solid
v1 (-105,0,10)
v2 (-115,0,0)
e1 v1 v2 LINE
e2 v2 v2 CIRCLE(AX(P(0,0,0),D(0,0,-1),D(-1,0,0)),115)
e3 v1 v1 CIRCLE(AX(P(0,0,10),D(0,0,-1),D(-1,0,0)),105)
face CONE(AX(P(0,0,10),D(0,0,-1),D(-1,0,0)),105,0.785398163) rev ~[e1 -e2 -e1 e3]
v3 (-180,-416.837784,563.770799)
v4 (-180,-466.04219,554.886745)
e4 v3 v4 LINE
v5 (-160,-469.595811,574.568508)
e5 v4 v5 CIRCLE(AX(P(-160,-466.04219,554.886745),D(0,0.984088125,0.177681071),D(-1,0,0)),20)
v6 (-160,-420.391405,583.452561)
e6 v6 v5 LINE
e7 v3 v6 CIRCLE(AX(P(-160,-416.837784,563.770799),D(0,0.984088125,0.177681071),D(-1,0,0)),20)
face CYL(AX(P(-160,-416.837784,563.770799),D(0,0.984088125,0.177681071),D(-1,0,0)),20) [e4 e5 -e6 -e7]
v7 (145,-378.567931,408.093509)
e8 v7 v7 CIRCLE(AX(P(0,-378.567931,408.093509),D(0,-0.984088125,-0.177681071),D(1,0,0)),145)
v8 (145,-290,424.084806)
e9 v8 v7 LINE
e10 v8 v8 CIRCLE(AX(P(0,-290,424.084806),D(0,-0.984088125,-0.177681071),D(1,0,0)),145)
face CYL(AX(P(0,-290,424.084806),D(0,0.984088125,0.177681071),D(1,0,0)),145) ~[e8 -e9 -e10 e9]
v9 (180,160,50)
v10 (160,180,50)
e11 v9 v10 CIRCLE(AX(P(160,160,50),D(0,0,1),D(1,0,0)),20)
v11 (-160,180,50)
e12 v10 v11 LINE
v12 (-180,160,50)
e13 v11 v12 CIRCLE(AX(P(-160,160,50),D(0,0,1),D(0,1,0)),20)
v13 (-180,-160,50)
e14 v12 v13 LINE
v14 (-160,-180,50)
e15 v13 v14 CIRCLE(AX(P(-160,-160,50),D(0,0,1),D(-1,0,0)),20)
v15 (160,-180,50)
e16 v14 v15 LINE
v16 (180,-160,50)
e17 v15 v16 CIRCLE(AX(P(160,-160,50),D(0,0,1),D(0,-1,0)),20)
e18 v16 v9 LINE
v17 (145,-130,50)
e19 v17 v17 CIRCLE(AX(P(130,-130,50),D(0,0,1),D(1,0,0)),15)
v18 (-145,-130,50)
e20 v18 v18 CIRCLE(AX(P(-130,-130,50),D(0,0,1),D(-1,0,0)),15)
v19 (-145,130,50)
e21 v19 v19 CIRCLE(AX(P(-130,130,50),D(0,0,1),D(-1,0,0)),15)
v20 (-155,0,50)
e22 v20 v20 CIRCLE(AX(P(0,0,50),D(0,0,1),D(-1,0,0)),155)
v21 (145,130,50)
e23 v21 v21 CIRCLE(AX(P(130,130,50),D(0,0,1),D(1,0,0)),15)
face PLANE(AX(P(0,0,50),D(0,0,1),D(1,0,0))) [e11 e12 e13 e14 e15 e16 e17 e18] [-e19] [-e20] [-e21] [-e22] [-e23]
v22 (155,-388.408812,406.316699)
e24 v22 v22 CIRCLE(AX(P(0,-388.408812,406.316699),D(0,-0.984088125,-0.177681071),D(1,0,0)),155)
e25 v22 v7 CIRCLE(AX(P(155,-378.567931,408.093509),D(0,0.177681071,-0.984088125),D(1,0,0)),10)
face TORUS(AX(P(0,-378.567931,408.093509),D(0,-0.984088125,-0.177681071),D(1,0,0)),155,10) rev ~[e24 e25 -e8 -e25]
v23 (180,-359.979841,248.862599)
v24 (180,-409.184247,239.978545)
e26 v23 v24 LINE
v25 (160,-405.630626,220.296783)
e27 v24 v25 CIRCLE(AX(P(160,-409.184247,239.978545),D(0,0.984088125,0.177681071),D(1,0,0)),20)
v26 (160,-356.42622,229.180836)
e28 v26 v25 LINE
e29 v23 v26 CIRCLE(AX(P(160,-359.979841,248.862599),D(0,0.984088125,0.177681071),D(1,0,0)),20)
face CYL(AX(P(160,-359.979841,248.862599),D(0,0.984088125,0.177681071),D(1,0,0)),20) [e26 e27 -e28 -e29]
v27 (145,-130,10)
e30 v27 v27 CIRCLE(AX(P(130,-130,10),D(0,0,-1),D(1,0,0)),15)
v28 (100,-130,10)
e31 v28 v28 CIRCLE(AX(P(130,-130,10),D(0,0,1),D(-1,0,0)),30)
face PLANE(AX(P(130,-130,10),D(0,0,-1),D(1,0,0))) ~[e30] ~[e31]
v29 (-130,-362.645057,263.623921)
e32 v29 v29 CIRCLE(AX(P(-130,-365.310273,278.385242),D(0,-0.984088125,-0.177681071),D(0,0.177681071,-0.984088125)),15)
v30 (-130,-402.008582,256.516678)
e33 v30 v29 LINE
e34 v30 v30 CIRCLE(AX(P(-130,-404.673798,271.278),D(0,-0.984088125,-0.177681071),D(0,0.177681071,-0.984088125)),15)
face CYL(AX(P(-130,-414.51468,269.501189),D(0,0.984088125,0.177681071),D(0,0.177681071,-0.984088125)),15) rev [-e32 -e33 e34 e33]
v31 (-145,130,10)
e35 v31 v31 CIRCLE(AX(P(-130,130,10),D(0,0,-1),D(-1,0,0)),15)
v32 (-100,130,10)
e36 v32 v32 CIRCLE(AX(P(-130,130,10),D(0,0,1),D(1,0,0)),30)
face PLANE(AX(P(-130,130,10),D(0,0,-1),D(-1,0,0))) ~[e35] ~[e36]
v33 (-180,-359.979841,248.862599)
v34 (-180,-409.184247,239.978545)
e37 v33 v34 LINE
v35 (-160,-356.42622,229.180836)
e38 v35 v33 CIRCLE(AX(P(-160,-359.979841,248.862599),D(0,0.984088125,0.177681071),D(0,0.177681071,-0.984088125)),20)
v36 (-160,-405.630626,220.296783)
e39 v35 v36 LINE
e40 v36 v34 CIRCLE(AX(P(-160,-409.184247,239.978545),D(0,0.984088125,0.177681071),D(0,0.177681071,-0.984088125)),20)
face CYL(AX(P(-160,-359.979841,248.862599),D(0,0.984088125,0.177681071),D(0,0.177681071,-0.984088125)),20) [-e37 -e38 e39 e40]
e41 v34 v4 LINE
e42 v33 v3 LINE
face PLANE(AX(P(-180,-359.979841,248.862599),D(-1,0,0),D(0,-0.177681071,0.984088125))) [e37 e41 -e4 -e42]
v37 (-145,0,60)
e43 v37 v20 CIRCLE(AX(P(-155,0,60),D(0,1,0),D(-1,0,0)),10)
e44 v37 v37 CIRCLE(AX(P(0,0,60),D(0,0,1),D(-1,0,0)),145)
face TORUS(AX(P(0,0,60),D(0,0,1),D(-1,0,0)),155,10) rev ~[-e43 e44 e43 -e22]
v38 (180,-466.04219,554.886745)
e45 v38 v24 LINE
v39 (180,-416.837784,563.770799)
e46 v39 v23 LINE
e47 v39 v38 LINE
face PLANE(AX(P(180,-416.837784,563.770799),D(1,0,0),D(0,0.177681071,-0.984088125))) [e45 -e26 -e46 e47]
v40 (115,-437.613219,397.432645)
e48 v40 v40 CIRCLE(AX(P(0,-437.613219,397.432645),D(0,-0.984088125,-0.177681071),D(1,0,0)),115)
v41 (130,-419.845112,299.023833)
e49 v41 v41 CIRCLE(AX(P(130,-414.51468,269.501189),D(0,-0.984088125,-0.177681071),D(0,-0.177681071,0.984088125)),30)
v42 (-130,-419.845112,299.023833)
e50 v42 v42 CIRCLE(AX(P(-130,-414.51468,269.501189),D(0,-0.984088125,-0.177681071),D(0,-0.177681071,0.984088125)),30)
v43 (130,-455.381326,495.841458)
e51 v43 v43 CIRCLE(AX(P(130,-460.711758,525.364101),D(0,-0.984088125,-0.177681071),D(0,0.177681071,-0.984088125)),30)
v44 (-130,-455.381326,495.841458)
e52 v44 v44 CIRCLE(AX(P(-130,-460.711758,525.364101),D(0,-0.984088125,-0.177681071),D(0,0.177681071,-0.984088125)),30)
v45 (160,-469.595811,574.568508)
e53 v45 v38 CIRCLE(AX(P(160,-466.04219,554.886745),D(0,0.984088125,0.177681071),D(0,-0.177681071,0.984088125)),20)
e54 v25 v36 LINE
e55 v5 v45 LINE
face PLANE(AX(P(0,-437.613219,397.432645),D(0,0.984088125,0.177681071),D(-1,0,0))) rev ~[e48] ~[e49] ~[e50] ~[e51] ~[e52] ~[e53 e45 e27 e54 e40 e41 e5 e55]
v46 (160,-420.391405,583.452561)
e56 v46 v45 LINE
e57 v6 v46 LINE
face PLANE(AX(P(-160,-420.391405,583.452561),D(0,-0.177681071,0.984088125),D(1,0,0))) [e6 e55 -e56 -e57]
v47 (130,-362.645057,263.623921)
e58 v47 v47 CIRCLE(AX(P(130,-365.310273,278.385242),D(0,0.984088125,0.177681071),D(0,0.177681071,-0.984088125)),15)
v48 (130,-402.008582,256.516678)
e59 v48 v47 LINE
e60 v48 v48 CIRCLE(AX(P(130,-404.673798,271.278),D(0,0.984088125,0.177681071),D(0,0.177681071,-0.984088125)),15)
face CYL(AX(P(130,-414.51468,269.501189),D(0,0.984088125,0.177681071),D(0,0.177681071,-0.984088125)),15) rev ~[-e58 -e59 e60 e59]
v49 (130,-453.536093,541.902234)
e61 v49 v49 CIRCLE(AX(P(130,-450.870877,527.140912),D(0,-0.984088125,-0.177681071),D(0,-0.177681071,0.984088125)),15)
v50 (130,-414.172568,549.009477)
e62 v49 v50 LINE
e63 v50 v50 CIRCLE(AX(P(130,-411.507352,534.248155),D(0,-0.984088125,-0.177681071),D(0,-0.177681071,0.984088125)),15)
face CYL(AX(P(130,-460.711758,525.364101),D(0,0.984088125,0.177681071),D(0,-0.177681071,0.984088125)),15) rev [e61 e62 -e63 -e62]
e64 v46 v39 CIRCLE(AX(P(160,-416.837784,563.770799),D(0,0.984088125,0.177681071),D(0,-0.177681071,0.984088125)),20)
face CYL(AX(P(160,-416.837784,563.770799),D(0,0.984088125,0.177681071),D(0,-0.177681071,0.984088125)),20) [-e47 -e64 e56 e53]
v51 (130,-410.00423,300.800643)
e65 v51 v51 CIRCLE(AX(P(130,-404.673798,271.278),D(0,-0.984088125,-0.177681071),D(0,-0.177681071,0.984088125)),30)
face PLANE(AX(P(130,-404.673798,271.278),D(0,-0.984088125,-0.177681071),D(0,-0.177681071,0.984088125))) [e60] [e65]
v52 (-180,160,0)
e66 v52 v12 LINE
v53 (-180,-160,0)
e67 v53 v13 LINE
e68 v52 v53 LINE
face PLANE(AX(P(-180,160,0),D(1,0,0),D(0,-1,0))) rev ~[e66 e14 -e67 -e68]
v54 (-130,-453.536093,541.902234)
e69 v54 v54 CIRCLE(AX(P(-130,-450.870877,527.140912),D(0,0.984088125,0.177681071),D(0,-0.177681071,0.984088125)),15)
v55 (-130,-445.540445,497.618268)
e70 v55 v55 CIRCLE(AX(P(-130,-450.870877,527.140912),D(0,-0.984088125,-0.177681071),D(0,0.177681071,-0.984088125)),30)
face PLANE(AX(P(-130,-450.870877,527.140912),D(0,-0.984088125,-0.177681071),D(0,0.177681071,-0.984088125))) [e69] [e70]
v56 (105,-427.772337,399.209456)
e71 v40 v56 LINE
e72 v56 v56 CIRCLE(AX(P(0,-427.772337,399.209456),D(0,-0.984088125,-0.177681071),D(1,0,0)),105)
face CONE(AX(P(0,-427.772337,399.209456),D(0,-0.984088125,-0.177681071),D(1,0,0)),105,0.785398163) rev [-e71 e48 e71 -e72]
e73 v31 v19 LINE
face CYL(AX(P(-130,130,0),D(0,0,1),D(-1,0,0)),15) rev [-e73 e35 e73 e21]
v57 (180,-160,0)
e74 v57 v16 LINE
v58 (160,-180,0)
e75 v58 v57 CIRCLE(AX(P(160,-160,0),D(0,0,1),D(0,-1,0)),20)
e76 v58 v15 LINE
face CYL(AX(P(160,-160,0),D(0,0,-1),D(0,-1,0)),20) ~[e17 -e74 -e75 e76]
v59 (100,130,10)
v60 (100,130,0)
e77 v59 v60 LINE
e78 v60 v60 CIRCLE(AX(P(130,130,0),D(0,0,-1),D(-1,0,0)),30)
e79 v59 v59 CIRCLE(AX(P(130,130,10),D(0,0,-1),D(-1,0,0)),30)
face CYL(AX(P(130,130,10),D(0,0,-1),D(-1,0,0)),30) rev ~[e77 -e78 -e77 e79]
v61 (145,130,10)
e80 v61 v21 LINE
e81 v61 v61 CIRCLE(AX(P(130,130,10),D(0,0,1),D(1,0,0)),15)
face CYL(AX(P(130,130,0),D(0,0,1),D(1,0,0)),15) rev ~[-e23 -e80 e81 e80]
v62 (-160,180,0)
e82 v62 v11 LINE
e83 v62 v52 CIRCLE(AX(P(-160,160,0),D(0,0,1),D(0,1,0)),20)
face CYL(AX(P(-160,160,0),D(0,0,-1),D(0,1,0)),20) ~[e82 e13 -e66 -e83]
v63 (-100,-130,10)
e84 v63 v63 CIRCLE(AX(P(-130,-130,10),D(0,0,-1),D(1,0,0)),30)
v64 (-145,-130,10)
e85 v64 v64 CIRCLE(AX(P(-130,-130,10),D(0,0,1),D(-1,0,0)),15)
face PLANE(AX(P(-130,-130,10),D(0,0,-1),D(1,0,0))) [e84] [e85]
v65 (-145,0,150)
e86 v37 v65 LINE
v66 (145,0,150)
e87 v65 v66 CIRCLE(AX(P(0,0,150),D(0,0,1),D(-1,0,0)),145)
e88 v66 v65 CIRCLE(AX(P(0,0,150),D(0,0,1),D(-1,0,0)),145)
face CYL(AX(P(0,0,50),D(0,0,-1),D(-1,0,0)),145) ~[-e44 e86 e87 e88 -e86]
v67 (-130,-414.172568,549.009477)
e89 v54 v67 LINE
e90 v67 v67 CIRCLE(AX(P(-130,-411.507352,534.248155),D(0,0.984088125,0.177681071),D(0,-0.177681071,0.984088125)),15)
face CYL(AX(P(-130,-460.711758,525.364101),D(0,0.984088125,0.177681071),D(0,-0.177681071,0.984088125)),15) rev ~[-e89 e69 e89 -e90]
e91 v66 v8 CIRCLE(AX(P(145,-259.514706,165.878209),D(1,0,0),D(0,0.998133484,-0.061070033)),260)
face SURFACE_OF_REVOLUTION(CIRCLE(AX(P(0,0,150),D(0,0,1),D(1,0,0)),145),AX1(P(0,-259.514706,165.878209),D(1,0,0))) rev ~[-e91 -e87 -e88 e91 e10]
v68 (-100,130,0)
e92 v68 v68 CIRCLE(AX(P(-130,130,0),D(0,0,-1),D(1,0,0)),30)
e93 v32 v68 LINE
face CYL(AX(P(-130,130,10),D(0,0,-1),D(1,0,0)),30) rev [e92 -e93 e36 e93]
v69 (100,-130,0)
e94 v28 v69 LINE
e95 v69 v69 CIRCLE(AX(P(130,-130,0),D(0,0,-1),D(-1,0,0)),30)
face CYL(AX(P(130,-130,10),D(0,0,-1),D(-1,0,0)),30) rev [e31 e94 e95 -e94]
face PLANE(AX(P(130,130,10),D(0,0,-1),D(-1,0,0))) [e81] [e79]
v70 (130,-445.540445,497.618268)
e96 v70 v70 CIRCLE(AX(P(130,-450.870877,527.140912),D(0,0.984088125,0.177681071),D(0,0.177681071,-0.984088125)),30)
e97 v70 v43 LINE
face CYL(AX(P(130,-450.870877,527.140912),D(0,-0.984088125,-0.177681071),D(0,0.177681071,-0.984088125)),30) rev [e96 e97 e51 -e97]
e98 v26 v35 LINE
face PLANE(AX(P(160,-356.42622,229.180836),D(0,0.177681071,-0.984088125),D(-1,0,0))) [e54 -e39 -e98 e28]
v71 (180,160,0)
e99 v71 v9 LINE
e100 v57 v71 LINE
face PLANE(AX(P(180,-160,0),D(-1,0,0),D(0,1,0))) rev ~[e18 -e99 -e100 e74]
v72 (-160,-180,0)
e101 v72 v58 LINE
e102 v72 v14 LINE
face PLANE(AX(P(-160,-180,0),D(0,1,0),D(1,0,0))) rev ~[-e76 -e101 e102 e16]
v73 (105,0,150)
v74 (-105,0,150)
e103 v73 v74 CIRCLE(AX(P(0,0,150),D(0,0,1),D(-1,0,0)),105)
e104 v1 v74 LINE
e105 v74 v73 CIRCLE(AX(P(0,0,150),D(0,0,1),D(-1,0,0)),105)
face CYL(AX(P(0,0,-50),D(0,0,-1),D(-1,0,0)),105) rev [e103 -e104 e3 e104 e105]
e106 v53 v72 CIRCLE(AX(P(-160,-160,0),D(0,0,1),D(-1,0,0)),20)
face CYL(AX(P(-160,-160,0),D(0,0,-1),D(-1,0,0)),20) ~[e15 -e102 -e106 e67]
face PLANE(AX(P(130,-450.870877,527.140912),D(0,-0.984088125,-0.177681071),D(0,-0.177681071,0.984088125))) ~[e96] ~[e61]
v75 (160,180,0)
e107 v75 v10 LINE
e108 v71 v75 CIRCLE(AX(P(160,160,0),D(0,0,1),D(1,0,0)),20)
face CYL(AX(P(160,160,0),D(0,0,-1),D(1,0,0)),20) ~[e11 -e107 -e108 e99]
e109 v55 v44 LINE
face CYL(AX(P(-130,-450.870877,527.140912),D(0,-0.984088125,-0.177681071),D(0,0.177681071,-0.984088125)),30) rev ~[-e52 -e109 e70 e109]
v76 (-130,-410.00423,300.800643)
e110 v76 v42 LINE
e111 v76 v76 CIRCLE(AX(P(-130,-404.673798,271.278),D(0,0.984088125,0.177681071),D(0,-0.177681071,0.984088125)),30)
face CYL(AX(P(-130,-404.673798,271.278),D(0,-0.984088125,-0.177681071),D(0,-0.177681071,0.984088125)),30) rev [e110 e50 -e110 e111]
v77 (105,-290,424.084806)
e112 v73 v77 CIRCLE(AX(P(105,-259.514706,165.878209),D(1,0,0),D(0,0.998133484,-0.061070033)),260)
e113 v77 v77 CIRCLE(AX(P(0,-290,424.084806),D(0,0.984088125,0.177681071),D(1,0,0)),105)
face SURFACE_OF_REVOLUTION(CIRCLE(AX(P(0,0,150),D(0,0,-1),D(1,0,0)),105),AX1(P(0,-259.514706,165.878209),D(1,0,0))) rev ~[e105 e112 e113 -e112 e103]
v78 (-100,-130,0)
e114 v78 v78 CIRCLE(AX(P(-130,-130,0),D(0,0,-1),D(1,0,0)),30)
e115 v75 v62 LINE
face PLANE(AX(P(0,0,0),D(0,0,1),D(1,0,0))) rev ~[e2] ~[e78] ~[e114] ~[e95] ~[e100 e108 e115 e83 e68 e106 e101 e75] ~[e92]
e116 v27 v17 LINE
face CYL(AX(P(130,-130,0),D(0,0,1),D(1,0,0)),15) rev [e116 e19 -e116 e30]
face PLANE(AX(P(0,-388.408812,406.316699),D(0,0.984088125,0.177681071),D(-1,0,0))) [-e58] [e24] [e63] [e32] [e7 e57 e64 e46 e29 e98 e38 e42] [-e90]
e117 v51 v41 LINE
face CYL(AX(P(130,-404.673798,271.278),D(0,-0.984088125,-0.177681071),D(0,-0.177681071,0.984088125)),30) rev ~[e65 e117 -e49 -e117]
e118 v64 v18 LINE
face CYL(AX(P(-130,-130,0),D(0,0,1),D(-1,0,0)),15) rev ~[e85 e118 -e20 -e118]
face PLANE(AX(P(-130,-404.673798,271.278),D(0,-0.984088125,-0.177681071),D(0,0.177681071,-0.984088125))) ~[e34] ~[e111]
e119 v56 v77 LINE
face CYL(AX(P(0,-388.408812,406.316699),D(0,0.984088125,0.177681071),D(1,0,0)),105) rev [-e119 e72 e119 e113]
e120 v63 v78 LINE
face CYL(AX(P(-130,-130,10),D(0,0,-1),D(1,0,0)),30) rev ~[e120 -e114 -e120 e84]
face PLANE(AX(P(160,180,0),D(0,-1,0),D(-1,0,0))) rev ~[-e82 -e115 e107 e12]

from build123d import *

# Parameters (mm, degrees)
INLET_FLANGE_360X360X50_DEPTH                    = 50
INLET_HUB_SKETCH_R                               = 145
INLET_HUB_SKETCH_R_2                             = 105
INLET_HUB_290_DEPTH                              = 100
INLET_START                                      = -100
INLET_BORE_SKETCH_R                              = 105
INLET_BORE_CUT_DEPTH                             = 100
INLET_FLANGE_CHAMFER_10_SIZE                     = 10
INLET_FLANGE_C_BORE_HOLE_30_D                    = 30
INLET_FLANGE_C_BORE_HOLE_30_CBORE_D              = 60
INLET_FLANGE_C_BORE_HOLE_30_CBORE_DEPTH          = 10
INLET_HOLES_MIRROR_RIGHT_COPY_1_D                = 30
INLET_HOLES_MIRROR_RIGHT_COPY_1_CBORE_D          = 60
INLET_HOLES_MIRROR_RIGHT_COPY_1_CBORE_DEPTH      = 10
BEND_PROFILE_SKETCH_R                            = 145
BEND_PROFILE_SKETCH_R_2                          = 105
OUTLET_HUB_SKETCH_R                              = 145
OUTLET_HUB_SKETCH_R_2                            = 105
OUTLET_HUB_290_DEPTH                             = 100
OUTLET_FLANGE_SKETCH_R                           = 105
OUTLET_FLANGE_360X360X50_DEPTH                   = 50
OUTLET_FLANGE_C_BORE_HOLE_30_D                   = 30
OUTLET_FLANGE_C_BORE_HOLE_30_DEPTH               = 50
OUTLET_FLANGE_C_BORE_HOLE_30_CBORE_D             = 60
OUTLET_FLANGE_C_BORE_HOLE_30_CBORE_DEPTH         = 10
OUTLET_HOLES_MIRROR_MID_PLANE_COPY_1_D           = 30
OUTLET_HOLES_MIRROR_MID_PLANE_COPY_1_DEPTH       = 50
OUTLET_HOLES_MIRROR_MID_PLANE_COPY_1_CBORE_D     = 60
OUTLET_HOLES_MIRROR_MID_PLANE_COPY_1_CBORE_DEPTH = 10
HUB_FILLETS_R10_R                                = 10
OUTLET_FLANGE_CHAMFER_10_SIZE                    = 10


with BuildPart() as part:
    # Inlet Flange Sketch → Inlet Flange 360x360x50 (new body)
    with BuildSketch(Plane.XY):
        with BuildLine():
            Line((-160, -180), (160, -180))
            ThreePointArc((160, -180), (174.142135624, -174.142135624), (180, -160))
            Line((180, -160), (180, 160))
            ThreePointArc((180, 160), (174.142135624, 174.142135624), (160, 180))
            Line((160, 180), (-160, 180))
            ThreePointArc((-160, 180), (-174.142135624, 174.142135624), (-180, 160))
            Line((-180, 160), (-180, -160))
            ThreePointArc((-180, -160), (-174.142135624, -174.142135624), (-160, -180))
        make_face()
    extrude(amount=INLET_FLANGE_360X360X50_DEPTH)

    # Inlet Hub Sketch → Inlet Hub Ø290 (add)
    with BuildSketch(Plane.XY.offset(50)):
        with Locations(Location((0, 0, 0), (0, 0, 180))):
            Circle(INLET_HUB_SKETCH_R)
        with Locations(Location((0, 0, 0), (0, 0, 180))):
            Circle(INLET_HUB_SKETCH_R_2, mode=Mode.SUBTRACT)
    extrude(amount=INLET_HUB_290_DEPTH)

    # Inlet Bore Sketch → Inlet Bore Cut (cut)
    with BuildSketch(Plane.XY.offset(50).offset(INLET_START)):
        with Locations(Location((0, 0, 0), (0, 0, 180))):
            Circle(INLET_BORE_SKETCH_R)
    extrude(amount=INLET_BORE_CUT_DEPTH, mode=Mode.SUBTRACT)

    # Inlet Flange Chamfer 10
    inlet_flange_chamfer_10_edges = [part.edges().sort_by_distance(p)[0] for p in [
        (105, 0, 0),
    ]]
    chamfer(inlet_flange_chamfer_10_edges, length=INLET_FLANGE_CHAMFER_10_SIZE)

    # Inlet Flange C-Bore Hole Ø30 (through all)
    with Locations(Plane(origin=(130, 130, 0), x_dir=(-1, 0, 0), z_dir=(0, 0, -1))):
        with Locations((0, 0)):
            inlet_flange_c_bore_hole_30 = CounterBoreHole(INLET_FLANGE_C_BORE_HOLE_30_D / 2, INLET_FLANGE_C_BORE_HOLE_30_CBORE_D / 2, INLET_FLANGE_C_BORE_HOLE_30_CBORE_DEPTH)

    # Inlet Holes Mirror Top: Inlet Flange C-Bore Hole Ø30 across plane
    add(inlet_flange_c_bore_hole_30.mirror(Plane.ZX), mode=Mode.SUBTRACT)

    # Inlet Holes Mirror Right: Inlet Flange C-Bore Hole Ø30 across plane
    add(inlet_flange_c_bore_hole_30.mirror(Plane(origin=(0, 0, 0), x_dir=(0, 0, 1), z_dir=(1, 0, 0))), mode=Mode.SUBTRACT)

    # Inlet Holes Mirror Right copy 1 (through all)
    with Locations(Plane(origin=(-130, -130, 0), x_dir=(1, 0, 0), z_dir=(0, 0, -1))):
        with Locations((0, 0)):
            CounterBoreHole(INLET_HOLES_MIRROR_RIGHT_COPY_1_D / 2, INLET_HOLES_MIRROR_RIGHT_COPY_1_CBORE_D / 2, INLET_HOLES_MIRROR_RIGHT_COPY_1_CBORE_DEPTH)

    # Pipe Bend Sweep: sweep along a path in Bend Path Sketch
    with BuildLine(Plane(origin=(0, 0, 0), x_dir=(0, 0, -1), z_dir=(1, 0, 0))) as pipe_bend_sweep_path:
        ThreePointArc((-150, 0), (-354.837892053, -80.925125926), (-424.084805758, -290))
    # Bend Profile Sketch → Pipe Bend Sweep (sweep)
    with BuildSketch(Plane.XY.offset(150)):
        Circle(BEND_PROFILE_SKETCH_R)
        Circle(BEND_PROFILE_SKETCH_R_2, mode=Mode.SUBTRACT)
    sweep(path=pipe_bend_sweep_path.line)

    # Outlet Hub Sketch → Outlet Hub Ø290 (add)
    with BuildSketch(Plane(origin=(0, -206.691683571, -37.319015141), x_dir=(1, 0, 0), z_dir=(0, -0.9840881246839114, -0.1776810706184051))):
        with Locations((0, 468.864331685)):
            Circle(OUTLET_HUB_SKETCH_R)
        with Locations((0, 468.864331685)):
            Circle(OUTLET_HUB_SKETCH_R_2, mode=Mode.SUBTRACT)
    extrude(amount=OUTLET_HUB_290_DEPTH)

    # Outlet Flange Sketch → Outlet Flange 360x360x50 (add)
    with BuildSketch(Plane(origin=(0, -305.10049604, -55.087122203), x_dir=(1, 0, 0), z_dir=(0, -0.9840881246839113, -0.17768107061840513))):
        with BuildLine():
            Line((-160, 648.864331685), (160, 648.864331685))
            ThreePointArc((160, 648.864331685), (174.142135624, 643.006467309), (180, 628.864331685))
            Line((180, 628.864331685), (180, 308.864331685))
            ThreePointArc((180, 308.864331685), (174.142135624, 294.722196061), (160, 288.864331685))
            Line((160, 288.864331685), (-160, 288.864331685))
            ThreePointArc((-160, 288.864331685), (-174.142135624, 294.722196061), (-180, 308.864331685))
            Line((-180, 308.864331685), (-180, 628.864331685))
            ThreePointArc((-180, 628.864331685), (-174.142135624, 643.006467309), (-160, 648.864331685))
        make_face()
        with Locations((0, 468.864331685)):
            Circle(OUTLET_FLANGE_SKETCH_R, mode=Mode.SUBTRACT)
    extrude(amount=OUTLET_FLANGE_360X360X50_DEPTH)

    # Outlet Flange C-Bore Hole Ø30
    with Locations(Plane(origin=(-130, -460.711757883, 525.364101375), x_dir=(0, 0.177681070618, -0.984088124684), z_dir=(0, -0.984088124684, -0.177681070618))):
        with Locations((0, 0)):
            outlet_flange_c_bore_hole_30 = CounterBoreHole(OUTLET_FLANGE_C_BORE_HOLE_30_D / 2, OUTLET_FLANGE_C_BORE_HOLE_30_CBORE_D / 2, OUTLET_FLANGE_C_BORE_HOLE_30_CBORE_DEPTH, depth=OUTLET_FLANGE_C_BORE_HOLE_30_DEPTH)

    # Outlet Holes Mirror Right: Outlet Flange C-Bore Hole Ø30 across plane
    add(outlet_flange_c_bore_hole_30.mirror(Plane(origin=(0, 0, 0), x_dir=(0, 0, 1), z_dir=(1, 0, 0))), mode=Mode.SUBTRACT)

    # Outlet Holes Mirror Mid Plane: Outlet Flange C-Bore Hole Ø30 across plane
    add(outlet_flange_c_bore_hole_30.mirror(Plane(origin=(0, -83.308316429, 461.403820899), x_dir=(1, 0, 0), z_dir=(0, -0.17768107061840513, 0.9840881246839113))), mode=Mode.SUBTRACT)

    # Outlet Holes Mirror Mid Plane copy 1
    with Locations(Plane(origin=(130, -414.514679522, 269.501188956), x_dir=(0, -0.17768107061881563, 0.9840881246838526), z_dir=(0, -0.9840881246838528, -0.17768107061881566))):
        with Locations((0, 0)):
            CounterBoreHole(OUTLET_HOLES_MIRROR_MID_PLANE_COPY_1_D / 2, OUTLET_HOLES_MIRROR_MID_PLANE_COPY_1_CBORE_D / 2, OUTLET_HOLES_MIRROR_MID_PLANE_COPY_1_CBORE_DEPTH, depth=OUTLET_HOLES_MIRROR_MID_PLANE_COPY_1_DEPTH)

    # Hub Fillets R10
    hub_fillets_r10_edges = [part.edges().sort_by_distance(p)[0] for p in [
        (145, 0, 50),
        (-145, -388.408812468, 406.316698697),
    ]]
    fillet(hub_fillets_r10_edges, radius=HUB_FILLETS_R10_R)

    # Outlet Flange Chamfer 10
    outlet_flange_chamfer_10_edges = [part.edges().sort_by_distance(p)[0] for p in [
        (-105, -437.613218703, 397.432645166),
    ]]
    chamfer(outlet_flange_chamfer_10_edges, length=OUTLET_FLANGE_CHAMFER_10_SIZE)


solid = part.part
